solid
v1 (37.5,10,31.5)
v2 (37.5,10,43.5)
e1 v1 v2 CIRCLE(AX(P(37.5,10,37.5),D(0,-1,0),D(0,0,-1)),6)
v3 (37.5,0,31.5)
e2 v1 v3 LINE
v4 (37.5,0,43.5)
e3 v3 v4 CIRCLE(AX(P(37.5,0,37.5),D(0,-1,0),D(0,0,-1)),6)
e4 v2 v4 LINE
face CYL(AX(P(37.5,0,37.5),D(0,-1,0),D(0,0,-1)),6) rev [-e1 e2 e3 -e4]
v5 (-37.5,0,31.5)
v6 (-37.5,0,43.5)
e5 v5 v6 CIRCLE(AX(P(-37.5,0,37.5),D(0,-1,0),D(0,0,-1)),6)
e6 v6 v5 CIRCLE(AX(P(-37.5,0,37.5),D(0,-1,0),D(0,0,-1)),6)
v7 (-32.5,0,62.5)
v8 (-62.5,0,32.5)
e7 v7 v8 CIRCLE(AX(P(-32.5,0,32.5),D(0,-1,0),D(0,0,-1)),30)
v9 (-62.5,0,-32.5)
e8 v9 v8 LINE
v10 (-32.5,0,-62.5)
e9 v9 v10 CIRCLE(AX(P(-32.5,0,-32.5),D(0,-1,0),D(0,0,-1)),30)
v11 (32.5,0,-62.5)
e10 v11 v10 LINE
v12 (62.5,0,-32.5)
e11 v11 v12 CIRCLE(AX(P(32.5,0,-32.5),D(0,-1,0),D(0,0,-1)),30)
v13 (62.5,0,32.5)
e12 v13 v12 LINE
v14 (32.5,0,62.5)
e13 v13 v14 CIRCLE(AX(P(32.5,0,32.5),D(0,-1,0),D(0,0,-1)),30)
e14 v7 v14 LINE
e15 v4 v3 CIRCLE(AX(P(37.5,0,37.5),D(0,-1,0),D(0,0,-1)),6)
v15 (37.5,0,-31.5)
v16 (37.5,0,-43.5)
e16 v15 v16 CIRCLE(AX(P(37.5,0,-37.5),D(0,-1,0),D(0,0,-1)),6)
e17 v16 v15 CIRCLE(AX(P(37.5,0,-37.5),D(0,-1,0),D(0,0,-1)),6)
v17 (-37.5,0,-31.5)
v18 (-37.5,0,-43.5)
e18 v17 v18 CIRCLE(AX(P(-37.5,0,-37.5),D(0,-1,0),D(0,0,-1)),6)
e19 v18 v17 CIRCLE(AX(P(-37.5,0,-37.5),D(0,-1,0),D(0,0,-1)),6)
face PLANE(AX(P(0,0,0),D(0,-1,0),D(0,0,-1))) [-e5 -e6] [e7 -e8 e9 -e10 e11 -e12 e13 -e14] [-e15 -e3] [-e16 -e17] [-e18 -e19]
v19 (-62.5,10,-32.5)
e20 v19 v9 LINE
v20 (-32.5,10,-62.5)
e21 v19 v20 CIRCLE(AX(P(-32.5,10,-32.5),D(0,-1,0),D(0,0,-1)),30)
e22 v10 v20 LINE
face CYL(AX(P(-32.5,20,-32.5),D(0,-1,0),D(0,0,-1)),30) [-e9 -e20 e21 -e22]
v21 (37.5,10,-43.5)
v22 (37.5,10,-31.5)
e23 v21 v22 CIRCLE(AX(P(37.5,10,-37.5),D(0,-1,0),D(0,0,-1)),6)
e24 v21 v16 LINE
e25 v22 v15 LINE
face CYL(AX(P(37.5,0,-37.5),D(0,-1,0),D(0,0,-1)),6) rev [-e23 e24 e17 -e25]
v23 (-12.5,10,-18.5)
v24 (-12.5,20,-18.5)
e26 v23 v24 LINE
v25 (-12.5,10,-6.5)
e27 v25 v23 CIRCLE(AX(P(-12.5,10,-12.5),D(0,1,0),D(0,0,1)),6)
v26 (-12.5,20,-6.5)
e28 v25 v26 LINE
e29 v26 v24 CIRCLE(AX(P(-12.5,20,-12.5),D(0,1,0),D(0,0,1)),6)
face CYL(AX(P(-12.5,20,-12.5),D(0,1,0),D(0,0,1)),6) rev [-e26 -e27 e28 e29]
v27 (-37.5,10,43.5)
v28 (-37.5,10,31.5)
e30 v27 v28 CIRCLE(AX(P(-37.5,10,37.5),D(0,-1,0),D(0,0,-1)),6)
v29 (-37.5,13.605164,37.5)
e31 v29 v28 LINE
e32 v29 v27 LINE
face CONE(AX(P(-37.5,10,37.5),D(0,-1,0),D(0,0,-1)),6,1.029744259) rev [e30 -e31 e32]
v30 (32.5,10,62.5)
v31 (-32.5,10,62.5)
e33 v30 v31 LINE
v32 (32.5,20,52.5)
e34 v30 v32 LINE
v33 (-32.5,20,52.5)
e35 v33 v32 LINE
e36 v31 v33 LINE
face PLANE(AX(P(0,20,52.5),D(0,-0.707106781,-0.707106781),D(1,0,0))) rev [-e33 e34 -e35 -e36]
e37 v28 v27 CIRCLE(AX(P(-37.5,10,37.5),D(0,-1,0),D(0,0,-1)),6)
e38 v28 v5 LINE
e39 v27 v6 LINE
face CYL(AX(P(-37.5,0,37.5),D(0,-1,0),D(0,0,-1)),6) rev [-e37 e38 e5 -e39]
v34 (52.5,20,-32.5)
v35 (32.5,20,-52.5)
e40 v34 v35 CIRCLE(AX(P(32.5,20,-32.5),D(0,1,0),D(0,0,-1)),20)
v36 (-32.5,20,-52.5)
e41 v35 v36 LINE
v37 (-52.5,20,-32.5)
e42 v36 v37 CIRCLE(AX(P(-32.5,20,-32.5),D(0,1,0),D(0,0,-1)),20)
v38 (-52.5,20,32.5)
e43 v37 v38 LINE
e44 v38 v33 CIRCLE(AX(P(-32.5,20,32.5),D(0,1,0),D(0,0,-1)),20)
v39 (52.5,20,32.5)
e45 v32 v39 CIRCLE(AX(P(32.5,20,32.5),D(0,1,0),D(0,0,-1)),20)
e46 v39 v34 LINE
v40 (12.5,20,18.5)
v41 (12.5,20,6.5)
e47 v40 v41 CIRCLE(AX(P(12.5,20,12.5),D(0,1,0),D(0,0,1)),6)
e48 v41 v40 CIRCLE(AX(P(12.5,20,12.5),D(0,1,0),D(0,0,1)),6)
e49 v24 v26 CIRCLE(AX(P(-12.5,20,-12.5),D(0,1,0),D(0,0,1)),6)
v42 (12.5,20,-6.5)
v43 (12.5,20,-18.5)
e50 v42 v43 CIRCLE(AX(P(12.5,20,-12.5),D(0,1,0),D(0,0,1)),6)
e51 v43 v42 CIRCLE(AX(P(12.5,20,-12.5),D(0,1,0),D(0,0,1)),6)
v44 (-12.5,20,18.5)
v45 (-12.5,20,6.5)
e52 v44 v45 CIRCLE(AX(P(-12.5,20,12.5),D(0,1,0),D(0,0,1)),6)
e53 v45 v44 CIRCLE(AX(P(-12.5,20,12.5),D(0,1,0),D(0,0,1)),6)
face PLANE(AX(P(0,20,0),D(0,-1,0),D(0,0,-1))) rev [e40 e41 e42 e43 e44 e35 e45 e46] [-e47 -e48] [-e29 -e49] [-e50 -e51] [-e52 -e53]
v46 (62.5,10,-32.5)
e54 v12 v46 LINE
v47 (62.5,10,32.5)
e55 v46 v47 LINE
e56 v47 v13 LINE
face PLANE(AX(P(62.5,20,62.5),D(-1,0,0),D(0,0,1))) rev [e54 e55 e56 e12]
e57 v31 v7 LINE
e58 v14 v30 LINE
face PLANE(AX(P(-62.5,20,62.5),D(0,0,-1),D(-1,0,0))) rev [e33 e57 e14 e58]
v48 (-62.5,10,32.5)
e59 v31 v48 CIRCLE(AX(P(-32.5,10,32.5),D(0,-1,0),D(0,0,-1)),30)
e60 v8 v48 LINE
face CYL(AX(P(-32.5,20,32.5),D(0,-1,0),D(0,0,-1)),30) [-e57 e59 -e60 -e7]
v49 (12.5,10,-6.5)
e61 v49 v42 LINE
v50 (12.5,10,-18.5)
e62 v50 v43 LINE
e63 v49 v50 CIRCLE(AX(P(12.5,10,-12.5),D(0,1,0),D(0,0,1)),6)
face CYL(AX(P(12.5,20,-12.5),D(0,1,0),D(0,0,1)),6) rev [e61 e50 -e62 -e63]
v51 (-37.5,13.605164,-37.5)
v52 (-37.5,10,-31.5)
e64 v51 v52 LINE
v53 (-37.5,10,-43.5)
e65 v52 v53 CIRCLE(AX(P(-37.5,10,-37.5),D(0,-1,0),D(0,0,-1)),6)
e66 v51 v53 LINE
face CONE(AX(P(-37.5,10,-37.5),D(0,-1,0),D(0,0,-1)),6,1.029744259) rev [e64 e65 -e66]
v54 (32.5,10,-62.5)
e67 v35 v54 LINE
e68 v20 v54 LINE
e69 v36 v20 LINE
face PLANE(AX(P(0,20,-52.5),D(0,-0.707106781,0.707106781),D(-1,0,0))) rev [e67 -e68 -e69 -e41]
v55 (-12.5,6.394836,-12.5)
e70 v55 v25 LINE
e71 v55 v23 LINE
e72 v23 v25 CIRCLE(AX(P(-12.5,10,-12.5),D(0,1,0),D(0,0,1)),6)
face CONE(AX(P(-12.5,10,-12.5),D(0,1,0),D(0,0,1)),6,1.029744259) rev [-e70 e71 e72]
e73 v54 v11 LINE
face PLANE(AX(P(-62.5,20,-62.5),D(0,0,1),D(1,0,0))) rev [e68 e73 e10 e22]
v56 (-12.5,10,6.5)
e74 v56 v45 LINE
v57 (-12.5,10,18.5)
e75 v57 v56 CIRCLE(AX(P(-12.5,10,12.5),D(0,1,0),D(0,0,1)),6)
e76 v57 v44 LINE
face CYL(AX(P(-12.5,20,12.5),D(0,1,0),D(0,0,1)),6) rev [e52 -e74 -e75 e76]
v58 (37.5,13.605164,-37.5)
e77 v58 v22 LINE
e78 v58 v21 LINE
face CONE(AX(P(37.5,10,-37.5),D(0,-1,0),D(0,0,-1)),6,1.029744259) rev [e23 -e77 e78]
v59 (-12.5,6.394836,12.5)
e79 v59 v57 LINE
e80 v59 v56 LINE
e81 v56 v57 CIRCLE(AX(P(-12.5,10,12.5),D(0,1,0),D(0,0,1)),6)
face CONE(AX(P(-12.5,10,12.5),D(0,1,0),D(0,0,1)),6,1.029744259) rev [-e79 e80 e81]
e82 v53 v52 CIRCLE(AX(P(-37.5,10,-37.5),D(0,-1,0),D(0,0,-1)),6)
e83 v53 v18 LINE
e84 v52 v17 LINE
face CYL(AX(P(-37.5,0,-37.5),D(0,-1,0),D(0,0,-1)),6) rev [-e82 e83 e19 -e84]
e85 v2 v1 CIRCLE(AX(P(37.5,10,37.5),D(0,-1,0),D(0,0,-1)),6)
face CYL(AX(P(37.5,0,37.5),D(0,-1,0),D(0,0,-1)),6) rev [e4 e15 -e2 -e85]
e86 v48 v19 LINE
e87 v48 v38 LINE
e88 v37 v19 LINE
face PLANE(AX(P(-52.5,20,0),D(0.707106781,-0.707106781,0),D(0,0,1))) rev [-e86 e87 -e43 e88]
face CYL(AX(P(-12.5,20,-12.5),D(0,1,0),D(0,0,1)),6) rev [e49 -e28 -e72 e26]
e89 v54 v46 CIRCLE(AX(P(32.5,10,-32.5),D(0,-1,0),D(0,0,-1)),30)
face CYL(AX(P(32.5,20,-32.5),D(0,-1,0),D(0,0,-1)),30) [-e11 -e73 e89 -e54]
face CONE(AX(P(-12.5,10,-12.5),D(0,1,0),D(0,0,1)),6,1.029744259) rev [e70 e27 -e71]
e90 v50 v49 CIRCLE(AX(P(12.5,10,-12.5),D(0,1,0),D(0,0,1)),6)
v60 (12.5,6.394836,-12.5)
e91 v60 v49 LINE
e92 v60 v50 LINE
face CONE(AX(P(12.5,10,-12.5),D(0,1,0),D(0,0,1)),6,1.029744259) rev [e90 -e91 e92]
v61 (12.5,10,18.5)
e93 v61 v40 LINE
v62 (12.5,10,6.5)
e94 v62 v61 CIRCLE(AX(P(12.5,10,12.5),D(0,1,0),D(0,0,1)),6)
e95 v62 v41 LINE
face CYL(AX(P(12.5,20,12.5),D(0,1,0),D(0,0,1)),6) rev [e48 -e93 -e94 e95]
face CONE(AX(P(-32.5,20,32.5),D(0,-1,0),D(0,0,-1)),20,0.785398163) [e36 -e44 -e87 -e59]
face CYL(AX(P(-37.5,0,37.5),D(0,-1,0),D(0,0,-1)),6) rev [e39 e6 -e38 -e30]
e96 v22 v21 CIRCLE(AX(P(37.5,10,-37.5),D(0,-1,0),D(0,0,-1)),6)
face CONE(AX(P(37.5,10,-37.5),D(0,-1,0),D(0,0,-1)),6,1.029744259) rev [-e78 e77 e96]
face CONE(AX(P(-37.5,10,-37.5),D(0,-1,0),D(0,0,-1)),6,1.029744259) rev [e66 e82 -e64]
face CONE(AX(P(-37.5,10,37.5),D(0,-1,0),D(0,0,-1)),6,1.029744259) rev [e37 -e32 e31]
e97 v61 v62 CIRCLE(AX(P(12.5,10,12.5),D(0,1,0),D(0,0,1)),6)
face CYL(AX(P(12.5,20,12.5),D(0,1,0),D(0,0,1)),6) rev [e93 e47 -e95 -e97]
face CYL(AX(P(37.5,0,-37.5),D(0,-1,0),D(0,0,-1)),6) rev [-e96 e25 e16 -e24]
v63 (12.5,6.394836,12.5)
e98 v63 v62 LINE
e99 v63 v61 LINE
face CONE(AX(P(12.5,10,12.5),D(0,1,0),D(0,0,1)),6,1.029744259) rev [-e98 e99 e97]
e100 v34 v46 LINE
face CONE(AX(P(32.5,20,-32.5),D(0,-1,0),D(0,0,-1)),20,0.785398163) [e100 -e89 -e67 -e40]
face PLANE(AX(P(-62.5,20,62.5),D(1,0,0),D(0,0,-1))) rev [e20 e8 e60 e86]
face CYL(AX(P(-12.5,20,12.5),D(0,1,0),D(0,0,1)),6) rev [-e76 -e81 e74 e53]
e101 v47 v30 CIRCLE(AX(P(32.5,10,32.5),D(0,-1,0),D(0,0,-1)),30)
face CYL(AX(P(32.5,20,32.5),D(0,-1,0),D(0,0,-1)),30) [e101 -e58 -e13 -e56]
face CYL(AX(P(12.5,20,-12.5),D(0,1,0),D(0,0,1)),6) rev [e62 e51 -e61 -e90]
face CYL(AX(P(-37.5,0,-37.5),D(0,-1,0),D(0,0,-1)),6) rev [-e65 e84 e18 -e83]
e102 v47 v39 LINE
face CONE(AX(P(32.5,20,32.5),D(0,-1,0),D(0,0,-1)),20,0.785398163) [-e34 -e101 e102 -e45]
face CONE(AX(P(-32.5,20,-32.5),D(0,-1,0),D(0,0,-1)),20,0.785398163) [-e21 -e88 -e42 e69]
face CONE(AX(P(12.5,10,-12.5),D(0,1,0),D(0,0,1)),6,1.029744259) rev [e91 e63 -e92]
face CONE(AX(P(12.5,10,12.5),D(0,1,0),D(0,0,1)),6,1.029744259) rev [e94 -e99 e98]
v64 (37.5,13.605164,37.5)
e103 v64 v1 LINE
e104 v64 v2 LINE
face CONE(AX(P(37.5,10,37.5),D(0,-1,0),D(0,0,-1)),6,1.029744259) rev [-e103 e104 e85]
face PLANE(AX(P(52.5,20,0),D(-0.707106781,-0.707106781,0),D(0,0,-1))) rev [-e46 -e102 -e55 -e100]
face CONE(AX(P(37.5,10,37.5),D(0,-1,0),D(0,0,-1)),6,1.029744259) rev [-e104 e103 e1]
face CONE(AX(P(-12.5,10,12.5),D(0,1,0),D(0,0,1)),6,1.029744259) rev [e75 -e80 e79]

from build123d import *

# Parameters (mm, degrees)
BASE_PLATE_PROFILE_125X125_W = 125
BASE_PLATE_PROFILE_125X125_H = 125
BASE_PLATE_20MM_DEPTH        = 20
CORNER_FILLETS_R30_R         = 30
EDGE_CHAMFER_10X45_SIZE      = 10
DOWEL_HOLES_12X10_A_D        = 12
DOWEL_HOLES_12X10_A_DEPTH    = 10
DOWEL_HOLES_12X10_A_TIP      = 3.605163714
DOWEL_HOLES_12X10_B_D        = 12
DOWEL_HOLES_12X10_B_DEPTH    = 10
DOWEL_HOLES_12X10_B_TIP      = 3.605163714


with BuildPart() as part:
    # Base Plate Profile 125x125 → Base Plate 20mm (new body)
    with BuildSketch(Plane(origin=(0, 0, 0), x_dir=(1, 0, 0), z_dir=(0, 1, 0))):
        Rectangle(BASE_PLATE_PROFILE_125X125_W, BASE_PLATE_PROFILE_125X125_H)
    extrude(amount=BASE_PLATE_20MM_DEPTH)

    # Corner Fillets R30
    corner_fillets_r30_edges = [part.edges().sort_by_distance(p)[0] for p in [
        (62.5, 10, 62.5),
        (-62.5, 10, 62.5),
        (-62.5, 10, -62.5),
        (62.5, 10, -62.5),
    ]]
    fillet(corner_fillets_r30_edges, radius=CORNER_FILLETS_R30_R)

    # Edge Chamfer 10x45°
    edge_chamfer_10x45_edges = [part.edges().sort_by_distance(p)[0] for p in [
        (-62.5, 20, 0),
        (0, 20, -62.5),
        (62.5, 20, 0),
        (0, 20, 62.5),
        (-53.713203436, 20, 53.713203436),
        (53.713203436, 20, 53.713203436),
        (53.713203436, 20, -53.713203436),
        (-53.713203436, 20, -53.713203436),
    ]]
    chamfer(edge_chamfer_10x45_edges, length=EDGE_CHAMFER_10X45_SIZE)

    # Dowel Holes Ø12x10 A
    with Locations(Plane(origin=(-12.5, 20, -12.5), x_dir=(0, 0, 1), z_dir=(0, 1, 0))):
        with Locations((0, 0), (0, 25), (25, 25), (25, 0)):
            Hole(DOWEL_HOLES_12X10_A_D / 2, depth=DOWEL_HOLES_12X10_A_DEPTH)
            with Locations((0, 0, -(DOWEL_HOLES_12X10_A_DEPTH + DOWEL_HOLES_12X10_A_TIP / 2))):  # 118° drill point
                Cone(0, DOWEL_HOLES_12X10_A_D / 2, DOWEL_HOLES_12X10_A_TIP, mode=Mode.SUBTRACT)

    # Dowel Holes Ø12x10 B
    with Locations(Plane(origin=(-37.5, 0, 37.5), x_dir=(0, 0, -1), z_dir=(0, -1, 0))):
        with Locations((0, 0), (0, 75), (75, 75), (75, 0)):
            Hole(DOWEL_HOLES_12X10_B_D / 2, depth=DOWEL_HOLES_12X10_B_DEPTH)
            with Locations((0, 0, -(DOWEL_HOLES_12X10_B_DEPTH + DOWEL_HOLES_12X10_B_TIP / 2))):  # 118° drill point
                Cone(0, DOWEL_HOLES_12X10_B_D / 2, DOWEL_HOLES_12X10_B_TIP, mode=Mode.SUBTRACT)


solid = part.part
